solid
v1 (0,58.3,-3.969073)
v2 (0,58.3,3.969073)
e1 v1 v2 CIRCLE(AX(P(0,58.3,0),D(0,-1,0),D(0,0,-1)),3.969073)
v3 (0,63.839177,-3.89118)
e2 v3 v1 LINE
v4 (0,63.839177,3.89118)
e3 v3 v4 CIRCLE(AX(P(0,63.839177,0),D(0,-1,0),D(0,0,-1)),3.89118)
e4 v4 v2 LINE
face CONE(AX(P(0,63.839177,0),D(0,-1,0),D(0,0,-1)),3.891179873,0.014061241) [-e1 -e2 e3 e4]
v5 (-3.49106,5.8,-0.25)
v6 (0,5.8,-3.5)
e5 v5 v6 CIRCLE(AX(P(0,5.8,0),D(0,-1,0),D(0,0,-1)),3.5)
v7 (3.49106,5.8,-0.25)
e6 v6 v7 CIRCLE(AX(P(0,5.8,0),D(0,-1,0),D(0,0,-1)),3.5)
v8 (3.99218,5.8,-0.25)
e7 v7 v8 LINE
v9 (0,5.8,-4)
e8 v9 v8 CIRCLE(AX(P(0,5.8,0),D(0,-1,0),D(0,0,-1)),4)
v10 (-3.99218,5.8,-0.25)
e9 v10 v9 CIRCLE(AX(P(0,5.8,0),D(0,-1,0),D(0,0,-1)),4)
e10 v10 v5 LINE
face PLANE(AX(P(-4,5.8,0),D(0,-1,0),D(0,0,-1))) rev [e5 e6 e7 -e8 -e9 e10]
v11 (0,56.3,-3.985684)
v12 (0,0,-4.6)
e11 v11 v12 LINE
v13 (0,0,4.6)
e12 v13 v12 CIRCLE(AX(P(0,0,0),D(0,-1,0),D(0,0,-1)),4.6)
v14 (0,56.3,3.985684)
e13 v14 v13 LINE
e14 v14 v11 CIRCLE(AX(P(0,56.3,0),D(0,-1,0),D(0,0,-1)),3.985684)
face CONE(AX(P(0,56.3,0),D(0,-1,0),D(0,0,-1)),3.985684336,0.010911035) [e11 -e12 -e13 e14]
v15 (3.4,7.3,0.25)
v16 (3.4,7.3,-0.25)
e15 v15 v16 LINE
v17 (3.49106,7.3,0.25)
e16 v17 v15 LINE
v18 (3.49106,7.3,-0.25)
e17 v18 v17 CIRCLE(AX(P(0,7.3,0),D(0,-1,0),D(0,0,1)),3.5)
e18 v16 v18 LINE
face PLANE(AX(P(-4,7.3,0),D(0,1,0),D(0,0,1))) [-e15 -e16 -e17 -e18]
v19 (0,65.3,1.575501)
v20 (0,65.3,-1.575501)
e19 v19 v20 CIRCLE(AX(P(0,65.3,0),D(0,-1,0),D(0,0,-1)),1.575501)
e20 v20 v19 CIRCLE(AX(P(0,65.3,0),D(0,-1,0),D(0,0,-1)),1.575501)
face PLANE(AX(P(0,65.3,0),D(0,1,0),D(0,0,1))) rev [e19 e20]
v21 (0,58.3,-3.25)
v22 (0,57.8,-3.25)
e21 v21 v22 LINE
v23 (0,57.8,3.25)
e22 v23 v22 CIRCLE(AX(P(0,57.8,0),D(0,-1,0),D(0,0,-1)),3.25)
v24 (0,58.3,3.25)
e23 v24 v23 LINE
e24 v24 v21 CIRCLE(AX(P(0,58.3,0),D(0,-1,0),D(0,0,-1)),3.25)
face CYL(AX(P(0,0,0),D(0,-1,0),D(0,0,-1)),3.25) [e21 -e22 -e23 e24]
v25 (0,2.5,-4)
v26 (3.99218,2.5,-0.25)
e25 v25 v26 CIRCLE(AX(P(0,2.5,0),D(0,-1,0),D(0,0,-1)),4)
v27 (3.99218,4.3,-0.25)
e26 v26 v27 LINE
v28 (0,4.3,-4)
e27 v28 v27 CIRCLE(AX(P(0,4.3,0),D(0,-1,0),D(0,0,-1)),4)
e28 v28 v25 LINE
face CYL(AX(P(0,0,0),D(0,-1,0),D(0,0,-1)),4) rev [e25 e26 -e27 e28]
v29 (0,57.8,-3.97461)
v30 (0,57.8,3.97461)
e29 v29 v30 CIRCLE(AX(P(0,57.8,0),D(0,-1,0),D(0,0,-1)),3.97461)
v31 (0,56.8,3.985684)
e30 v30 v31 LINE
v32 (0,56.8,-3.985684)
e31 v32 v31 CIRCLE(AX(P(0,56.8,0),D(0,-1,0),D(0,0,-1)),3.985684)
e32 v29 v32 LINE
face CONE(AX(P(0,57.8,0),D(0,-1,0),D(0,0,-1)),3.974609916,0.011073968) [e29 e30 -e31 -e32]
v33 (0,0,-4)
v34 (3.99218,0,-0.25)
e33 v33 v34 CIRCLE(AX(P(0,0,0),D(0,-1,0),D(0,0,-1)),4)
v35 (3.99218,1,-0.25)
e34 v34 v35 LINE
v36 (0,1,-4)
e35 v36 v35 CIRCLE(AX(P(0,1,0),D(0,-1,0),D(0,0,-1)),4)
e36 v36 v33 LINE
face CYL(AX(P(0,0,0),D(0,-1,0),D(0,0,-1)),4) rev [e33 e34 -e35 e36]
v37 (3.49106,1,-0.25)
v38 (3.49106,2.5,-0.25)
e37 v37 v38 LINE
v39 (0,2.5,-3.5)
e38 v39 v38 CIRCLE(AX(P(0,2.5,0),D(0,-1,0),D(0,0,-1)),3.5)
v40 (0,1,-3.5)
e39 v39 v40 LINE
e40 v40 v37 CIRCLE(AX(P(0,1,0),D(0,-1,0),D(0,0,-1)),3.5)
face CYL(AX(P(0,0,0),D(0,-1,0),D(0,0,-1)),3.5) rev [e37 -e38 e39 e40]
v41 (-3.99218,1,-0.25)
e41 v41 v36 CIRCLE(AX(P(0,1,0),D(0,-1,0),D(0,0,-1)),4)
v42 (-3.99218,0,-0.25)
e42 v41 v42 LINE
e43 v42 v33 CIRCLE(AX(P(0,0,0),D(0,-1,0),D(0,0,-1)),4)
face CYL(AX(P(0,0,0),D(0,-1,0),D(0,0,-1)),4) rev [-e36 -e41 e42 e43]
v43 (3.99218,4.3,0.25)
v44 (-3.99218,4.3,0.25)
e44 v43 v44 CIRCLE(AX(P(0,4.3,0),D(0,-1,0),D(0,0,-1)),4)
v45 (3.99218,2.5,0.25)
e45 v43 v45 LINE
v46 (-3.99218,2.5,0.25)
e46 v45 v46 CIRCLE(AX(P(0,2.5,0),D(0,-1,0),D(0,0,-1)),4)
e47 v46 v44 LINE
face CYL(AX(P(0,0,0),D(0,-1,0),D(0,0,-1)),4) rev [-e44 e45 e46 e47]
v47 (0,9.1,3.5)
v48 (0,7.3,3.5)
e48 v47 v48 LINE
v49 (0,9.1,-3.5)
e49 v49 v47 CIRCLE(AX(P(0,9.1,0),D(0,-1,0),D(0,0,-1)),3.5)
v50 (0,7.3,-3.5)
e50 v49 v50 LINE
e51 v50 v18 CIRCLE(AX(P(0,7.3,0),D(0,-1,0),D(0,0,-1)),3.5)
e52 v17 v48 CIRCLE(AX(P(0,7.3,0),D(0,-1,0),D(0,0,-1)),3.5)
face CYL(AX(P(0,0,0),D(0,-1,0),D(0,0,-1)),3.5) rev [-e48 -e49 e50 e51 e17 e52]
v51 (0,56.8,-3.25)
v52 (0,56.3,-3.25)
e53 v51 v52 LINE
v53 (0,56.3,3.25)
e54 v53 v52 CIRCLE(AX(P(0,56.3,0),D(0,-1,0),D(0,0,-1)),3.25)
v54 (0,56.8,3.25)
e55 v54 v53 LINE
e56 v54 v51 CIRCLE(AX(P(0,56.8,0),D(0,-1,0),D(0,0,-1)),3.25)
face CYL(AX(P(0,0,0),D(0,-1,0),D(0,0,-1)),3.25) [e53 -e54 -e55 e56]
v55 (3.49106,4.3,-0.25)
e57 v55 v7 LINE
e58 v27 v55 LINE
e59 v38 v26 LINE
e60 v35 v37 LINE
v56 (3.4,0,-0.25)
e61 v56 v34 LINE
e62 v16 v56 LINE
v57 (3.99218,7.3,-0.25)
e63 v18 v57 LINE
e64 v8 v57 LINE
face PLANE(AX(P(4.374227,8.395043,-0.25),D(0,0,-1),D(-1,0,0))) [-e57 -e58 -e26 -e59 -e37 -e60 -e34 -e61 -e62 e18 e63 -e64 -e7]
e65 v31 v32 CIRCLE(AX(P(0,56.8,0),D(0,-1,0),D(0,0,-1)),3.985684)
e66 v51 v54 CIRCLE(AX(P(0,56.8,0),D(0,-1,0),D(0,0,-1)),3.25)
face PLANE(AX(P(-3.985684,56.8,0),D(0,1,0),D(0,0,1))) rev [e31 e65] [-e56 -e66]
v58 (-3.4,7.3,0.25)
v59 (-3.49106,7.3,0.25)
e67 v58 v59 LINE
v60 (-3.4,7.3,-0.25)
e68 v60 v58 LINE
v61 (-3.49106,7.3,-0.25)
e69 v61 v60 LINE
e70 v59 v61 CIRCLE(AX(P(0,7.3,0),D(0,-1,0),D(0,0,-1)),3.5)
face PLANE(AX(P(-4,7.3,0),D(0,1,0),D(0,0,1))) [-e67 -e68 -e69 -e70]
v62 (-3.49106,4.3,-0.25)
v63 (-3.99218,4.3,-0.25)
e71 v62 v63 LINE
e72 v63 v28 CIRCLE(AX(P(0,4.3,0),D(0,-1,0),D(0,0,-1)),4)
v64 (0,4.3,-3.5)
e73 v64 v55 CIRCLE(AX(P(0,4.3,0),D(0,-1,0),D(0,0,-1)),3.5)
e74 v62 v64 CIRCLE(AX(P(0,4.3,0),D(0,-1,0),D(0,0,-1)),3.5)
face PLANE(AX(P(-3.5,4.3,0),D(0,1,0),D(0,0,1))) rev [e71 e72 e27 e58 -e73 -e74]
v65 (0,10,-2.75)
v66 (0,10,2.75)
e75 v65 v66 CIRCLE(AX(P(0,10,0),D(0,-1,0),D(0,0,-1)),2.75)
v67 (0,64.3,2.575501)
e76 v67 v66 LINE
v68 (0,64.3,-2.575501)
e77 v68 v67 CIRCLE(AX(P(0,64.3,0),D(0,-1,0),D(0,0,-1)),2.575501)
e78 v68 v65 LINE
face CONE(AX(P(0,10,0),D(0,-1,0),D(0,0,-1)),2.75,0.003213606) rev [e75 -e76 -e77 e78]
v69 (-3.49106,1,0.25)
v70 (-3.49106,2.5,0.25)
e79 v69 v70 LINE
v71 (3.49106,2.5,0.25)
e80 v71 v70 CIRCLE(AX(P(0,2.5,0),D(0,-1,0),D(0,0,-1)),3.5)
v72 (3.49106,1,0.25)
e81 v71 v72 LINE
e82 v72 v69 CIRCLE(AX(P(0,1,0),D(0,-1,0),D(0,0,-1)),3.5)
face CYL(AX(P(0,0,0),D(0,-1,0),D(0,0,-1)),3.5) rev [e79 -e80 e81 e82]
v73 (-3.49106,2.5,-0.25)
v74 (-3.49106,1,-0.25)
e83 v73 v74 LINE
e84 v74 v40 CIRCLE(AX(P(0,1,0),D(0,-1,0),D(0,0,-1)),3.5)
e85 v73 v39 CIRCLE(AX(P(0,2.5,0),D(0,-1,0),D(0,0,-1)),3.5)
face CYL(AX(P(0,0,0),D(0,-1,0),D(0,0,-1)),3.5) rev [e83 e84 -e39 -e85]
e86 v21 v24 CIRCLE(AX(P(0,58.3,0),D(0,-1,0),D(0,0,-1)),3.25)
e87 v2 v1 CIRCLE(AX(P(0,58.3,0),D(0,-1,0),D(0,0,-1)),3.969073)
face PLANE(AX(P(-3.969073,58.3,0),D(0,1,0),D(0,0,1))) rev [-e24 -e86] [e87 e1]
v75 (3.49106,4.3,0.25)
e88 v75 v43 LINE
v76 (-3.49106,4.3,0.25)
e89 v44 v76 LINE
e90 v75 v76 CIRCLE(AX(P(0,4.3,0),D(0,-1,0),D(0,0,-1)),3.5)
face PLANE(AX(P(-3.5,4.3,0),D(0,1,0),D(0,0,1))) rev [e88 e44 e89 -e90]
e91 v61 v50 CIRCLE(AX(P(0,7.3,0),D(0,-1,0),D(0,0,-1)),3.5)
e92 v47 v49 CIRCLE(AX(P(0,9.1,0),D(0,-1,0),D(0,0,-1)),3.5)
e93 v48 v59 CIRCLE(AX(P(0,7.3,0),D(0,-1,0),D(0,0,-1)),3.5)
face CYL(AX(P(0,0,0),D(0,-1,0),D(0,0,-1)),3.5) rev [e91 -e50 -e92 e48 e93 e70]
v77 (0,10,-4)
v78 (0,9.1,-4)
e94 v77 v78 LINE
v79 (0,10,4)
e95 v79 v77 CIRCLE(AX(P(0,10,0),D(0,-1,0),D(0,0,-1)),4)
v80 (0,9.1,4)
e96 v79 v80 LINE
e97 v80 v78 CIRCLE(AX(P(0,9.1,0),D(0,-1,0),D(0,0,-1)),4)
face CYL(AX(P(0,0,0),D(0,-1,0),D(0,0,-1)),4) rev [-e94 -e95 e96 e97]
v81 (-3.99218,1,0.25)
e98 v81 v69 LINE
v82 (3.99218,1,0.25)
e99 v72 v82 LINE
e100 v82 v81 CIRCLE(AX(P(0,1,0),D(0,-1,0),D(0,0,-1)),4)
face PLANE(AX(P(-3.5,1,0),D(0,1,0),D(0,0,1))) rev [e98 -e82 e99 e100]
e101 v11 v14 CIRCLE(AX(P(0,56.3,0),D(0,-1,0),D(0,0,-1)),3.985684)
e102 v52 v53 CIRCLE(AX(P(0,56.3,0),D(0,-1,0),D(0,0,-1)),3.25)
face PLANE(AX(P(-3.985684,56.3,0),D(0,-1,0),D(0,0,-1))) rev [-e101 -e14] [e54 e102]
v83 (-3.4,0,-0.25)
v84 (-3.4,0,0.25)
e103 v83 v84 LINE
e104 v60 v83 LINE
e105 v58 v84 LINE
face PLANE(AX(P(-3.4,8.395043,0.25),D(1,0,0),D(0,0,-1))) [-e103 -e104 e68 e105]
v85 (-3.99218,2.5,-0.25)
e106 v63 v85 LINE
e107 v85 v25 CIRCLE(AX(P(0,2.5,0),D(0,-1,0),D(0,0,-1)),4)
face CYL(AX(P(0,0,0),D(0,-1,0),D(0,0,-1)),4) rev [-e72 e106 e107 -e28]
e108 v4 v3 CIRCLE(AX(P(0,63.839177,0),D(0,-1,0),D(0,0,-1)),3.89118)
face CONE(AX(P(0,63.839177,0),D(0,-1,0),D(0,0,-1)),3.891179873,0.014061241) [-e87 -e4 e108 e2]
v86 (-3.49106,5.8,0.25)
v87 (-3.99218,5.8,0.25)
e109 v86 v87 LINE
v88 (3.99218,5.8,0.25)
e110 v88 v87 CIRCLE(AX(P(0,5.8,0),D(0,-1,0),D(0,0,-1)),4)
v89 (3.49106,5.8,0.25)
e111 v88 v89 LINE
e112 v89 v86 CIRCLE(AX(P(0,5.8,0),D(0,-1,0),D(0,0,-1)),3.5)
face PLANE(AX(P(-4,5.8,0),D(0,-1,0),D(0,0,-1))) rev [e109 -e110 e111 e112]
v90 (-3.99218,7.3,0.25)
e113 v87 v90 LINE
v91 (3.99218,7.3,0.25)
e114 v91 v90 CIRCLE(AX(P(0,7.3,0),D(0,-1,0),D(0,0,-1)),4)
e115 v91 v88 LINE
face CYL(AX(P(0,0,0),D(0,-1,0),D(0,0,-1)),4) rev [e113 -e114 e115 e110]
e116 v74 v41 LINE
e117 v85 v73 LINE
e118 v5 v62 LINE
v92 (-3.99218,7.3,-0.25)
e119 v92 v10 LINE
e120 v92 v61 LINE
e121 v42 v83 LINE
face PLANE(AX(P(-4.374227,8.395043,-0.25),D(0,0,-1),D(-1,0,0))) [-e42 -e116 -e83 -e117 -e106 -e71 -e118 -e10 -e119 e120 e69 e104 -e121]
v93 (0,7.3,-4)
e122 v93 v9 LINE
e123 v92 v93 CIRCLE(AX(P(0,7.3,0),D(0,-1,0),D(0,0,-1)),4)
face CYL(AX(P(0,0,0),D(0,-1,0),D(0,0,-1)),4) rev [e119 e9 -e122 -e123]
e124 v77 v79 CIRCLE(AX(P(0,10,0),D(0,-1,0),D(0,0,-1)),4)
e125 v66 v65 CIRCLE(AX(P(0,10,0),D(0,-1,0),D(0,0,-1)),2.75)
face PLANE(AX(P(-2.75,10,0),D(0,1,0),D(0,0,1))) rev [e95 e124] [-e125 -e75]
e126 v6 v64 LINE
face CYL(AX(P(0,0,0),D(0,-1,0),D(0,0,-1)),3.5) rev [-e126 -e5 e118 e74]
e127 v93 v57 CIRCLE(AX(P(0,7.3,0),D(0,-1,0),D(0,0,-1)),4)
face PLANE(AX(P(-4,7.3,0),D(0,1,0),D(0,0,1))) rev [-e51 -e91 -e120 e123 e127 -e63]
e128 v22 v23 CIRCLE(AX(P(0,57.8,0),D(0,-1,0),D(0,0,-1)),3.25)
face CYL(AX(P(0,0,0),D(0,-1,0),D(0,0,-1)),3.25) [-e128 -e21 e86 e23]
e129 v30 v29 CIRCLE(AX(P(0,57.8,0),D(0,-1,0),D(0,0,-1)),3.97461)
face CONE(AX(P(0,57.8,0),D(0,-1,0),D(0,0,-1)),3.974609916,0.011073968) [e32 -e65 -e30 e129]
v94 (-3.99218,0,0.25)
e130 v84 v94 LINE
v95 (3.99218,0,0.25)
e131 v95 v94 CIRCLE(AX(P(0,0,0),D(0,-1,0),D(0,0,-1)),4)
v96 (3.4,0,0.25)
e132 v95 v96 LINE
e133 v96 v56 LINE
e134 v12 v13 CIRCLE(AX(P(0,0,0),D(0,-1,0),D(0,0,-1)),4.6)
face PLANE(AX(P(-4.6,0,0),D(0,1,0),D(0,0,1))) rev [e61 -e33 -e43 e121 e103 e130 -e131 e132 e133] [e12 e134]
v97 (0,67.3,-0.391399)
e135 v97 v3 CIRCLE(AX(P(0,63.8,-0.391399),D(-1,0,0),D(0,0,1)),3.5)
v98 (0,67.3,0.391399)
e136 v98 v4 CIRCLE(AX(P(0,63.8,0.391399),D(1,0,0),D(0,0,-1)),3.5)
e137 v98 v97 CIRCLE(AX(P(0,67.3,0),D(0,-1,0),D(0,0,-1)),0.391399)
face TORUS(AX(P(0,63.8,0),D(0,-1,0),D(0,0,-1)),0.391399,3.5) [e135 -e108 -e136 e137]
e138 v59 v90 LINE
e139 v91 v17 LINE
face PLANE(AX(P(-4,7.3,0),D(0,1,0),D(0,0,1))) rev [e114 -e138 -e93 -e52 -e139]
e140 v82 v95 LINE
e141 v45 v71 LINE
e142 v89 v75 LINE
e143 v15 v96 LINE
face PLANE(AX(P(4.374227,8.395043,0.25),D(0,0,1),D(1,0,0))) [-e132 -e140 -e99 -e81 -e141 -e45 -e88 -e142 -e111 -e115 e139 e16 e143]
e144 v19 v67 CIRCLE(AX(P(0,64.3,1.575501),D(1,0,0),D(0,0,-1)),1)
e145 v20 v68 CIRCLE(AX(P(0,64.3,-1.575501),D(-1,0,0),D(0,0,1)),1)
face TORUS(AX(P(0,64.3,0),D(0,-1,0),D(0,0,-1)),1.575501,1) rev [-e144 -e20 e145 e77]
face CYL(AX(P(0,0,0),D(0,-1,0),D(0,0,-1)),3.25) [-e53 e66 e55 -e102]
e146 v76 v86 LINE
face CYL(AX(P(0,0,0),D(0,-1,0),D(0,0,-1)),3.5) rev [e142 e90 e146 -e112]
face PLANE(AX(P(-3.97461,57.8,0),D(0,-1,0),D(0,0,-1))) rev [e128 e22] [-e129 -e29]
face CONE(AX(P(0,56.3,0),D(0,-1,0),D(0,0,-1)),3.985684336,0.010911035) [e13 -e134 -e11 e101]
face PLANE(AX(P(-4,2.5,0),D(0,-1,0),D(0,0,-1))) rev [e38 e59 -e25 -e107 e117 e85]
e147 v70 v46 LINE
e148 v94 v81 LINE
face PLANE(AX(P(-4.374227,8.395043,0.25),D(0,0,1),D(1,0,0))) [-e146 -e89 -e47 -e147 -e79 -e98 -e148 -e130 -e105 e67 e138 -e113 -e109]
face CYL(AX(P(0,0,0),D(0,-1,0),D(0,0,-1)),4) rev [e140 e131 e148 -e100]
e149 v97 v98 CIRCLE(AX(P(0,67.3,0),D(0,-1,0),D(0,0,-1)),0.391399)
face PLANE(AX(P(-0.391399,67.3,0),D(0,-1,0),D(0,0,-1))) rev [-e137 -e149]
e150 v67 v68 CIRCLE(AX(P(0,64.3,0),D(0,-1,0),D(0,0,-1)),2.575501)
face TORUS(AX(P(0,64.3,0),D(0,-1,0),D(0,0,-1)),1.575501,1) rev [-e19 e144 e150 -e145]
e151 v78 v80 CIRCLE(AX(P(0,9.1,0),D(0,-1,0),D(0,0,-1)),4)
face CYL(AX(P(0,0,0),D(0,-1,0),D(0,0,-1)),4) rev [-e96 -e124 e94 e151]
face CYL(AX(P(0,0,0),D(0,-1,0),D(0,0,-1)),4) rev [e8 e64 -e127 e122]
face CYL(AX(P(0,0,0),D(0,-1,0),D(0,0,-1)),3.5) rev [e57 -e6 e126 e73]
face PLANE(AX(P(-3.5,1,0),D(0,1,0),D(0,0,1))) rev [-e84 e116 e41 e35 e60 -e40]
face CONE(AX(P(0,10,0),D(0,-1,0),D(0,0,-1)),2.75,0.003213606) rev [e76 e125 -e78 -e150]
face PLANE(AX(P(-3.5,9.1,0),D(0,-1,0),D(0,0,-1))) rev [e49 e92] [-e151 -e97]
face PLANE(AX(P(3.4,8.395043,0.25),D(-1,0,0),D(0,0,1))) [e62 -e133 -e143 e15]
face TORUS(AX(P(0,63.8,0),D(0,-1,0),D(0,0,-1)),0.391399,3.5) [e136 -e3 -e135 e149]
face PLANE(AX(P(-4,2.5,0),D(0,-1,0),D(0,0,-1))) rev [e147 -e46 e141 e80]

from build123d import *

# Parameters (mm, degrees)
EXTRUDE_1_REACH = 69.614
SKETCH_2_W      = 0.974227423
SKETCH_2_H      = 0.5


with BuildPart() as part:
    # 草图1 → 旋转1 (revolve)
    with BuildSketch(Plane.XY, mode=Mode.PRIVATE) as revolve_1_sk:
        with BuildLine():
            Line((-4.6, 0), (-4, 0))
            Line((-4, 0), (-4, 1))
            Line((-4, 1), (-3.5, 1))
            Line((-3.5, 1), (-3.5, 2.5))
            Line((-3.5, 2.5), (-4, 2.5))
            Line((-4, 2.5), (-4, 4.3))
            Line((-4, 4.3), (-3.5, 4.3))
            Line((-3.5, 4.3), (-3.5, 5.8))
            Line((-3.5, 5.8), (-4, 5.8))
            Line((-4, 5.8), (-4, 7.3))
            Line((-4, 7.3), (-3.5, 7.3))
            Line((-3.5, 7.3), (-3.5, 9.1))
            Line((-3.5, 9.1), (-4, 9.1))
            Line((-4, 9.1), (-4, 10))
            Line((-4, 10), (-2.75, 10))
            Line((-2.75, 10), (-2.575500592, 64.3))
            ThreePointArc((-2.575500592, 64.3), (-2.282607373, 65.007106781), (-1.575500592, 65.3))
            Line((-1.575500592, 65.3), (0, 65.3))
            Line((0, 65.3), (0, 67.3))
            Line((0, 67.3), (-0.391399138, 67.3))
            ThreePointArc((-0.391399138, 67.3), (-2.852382856, 66.288686228), (-3.891179873, 63.839176651))
            Line((-3.891179873, 63.839176651), (-3.969072705, 58.3))
            Line((-3.969072705, 58.3), (-3.25, 58.3))
            Line((-3.25, 58.3), (-3.25, 57.8))
            Line((-3.25, 57.8), (-3.974609916, 57.8))
            Line((-3.974609916, 57.8), (-3.985684336, 56.8))
            Line((-3.985684336, 56.8), (-3.25, 56.8))
            Line((-3.25, 56.8), (-3.25, 56.3))
            Line((-3.25, 56.3), (-3.985684336, 56.3))
            Line((-3.985684336, 56.3), (-4.6, 0))
        make_face()
    revolve(revolve_1_sk.sketch.rotate(Axis((0, 0, 0), (0, 1, 0)), 270), axis=Axis((0, 0, 0), (0, 1, 0)))

    # 凸台-拉伸1: up to this face of the body (flat: up to its plane)
    extrude_1_end = Plane(part.part.faces().sort_by_distance((0, 7.3, 3.886862915))[0])
    # 草图2 → 凸台-拉伸1 (add, up to the picked face)
    with BuildSketch(Plane.XZ, mode=Mode.PRIVATE) as extrude_1_sk1:
        with Locations((-3.887113712, 0)):
            Rectangle(SKETCH_2_W, SKETCH_2_H)
    extrude_1_tool1 = split(extrude(extrude_1_sk1.sketch, amount=-EXTRUDE_1_REACH, mode=Mode.PRIVATE), bisect_by=extrude_1_end, keep=Keep.BOTH, mode=Mode.PRIVATE)
    # 草图2 → 凸台-拉伸1 (add, up to the picked face)
    with BuildSketch(Plane.XZ, mode=Mode.PRIVATE) as extrude_1_sk2:
        with Locations((3.887113712, 0)):
            Rectangle(SKETCH_2_W, SKETCH_2_H)
    extrude_1_tool2 = split(extrude(extrude_1_sk2.sketch, amount=-EXTRUDE_1_REACH, mode=Mode.PRIVATE), bisect_by=extrude_1_end, keep=Keep.BOTH, mode=Mode.PRIVATE)
    add(extrude_1_tool1.solids().sort_by(Axis((-3.887114, 0, 0), (0, 1, 0)))[0])
    add(extrude_1_tool2.solids().sort_by(Axis((3.887114, 0, 0), (0, 1, 0)))[0])


solid = part.part
